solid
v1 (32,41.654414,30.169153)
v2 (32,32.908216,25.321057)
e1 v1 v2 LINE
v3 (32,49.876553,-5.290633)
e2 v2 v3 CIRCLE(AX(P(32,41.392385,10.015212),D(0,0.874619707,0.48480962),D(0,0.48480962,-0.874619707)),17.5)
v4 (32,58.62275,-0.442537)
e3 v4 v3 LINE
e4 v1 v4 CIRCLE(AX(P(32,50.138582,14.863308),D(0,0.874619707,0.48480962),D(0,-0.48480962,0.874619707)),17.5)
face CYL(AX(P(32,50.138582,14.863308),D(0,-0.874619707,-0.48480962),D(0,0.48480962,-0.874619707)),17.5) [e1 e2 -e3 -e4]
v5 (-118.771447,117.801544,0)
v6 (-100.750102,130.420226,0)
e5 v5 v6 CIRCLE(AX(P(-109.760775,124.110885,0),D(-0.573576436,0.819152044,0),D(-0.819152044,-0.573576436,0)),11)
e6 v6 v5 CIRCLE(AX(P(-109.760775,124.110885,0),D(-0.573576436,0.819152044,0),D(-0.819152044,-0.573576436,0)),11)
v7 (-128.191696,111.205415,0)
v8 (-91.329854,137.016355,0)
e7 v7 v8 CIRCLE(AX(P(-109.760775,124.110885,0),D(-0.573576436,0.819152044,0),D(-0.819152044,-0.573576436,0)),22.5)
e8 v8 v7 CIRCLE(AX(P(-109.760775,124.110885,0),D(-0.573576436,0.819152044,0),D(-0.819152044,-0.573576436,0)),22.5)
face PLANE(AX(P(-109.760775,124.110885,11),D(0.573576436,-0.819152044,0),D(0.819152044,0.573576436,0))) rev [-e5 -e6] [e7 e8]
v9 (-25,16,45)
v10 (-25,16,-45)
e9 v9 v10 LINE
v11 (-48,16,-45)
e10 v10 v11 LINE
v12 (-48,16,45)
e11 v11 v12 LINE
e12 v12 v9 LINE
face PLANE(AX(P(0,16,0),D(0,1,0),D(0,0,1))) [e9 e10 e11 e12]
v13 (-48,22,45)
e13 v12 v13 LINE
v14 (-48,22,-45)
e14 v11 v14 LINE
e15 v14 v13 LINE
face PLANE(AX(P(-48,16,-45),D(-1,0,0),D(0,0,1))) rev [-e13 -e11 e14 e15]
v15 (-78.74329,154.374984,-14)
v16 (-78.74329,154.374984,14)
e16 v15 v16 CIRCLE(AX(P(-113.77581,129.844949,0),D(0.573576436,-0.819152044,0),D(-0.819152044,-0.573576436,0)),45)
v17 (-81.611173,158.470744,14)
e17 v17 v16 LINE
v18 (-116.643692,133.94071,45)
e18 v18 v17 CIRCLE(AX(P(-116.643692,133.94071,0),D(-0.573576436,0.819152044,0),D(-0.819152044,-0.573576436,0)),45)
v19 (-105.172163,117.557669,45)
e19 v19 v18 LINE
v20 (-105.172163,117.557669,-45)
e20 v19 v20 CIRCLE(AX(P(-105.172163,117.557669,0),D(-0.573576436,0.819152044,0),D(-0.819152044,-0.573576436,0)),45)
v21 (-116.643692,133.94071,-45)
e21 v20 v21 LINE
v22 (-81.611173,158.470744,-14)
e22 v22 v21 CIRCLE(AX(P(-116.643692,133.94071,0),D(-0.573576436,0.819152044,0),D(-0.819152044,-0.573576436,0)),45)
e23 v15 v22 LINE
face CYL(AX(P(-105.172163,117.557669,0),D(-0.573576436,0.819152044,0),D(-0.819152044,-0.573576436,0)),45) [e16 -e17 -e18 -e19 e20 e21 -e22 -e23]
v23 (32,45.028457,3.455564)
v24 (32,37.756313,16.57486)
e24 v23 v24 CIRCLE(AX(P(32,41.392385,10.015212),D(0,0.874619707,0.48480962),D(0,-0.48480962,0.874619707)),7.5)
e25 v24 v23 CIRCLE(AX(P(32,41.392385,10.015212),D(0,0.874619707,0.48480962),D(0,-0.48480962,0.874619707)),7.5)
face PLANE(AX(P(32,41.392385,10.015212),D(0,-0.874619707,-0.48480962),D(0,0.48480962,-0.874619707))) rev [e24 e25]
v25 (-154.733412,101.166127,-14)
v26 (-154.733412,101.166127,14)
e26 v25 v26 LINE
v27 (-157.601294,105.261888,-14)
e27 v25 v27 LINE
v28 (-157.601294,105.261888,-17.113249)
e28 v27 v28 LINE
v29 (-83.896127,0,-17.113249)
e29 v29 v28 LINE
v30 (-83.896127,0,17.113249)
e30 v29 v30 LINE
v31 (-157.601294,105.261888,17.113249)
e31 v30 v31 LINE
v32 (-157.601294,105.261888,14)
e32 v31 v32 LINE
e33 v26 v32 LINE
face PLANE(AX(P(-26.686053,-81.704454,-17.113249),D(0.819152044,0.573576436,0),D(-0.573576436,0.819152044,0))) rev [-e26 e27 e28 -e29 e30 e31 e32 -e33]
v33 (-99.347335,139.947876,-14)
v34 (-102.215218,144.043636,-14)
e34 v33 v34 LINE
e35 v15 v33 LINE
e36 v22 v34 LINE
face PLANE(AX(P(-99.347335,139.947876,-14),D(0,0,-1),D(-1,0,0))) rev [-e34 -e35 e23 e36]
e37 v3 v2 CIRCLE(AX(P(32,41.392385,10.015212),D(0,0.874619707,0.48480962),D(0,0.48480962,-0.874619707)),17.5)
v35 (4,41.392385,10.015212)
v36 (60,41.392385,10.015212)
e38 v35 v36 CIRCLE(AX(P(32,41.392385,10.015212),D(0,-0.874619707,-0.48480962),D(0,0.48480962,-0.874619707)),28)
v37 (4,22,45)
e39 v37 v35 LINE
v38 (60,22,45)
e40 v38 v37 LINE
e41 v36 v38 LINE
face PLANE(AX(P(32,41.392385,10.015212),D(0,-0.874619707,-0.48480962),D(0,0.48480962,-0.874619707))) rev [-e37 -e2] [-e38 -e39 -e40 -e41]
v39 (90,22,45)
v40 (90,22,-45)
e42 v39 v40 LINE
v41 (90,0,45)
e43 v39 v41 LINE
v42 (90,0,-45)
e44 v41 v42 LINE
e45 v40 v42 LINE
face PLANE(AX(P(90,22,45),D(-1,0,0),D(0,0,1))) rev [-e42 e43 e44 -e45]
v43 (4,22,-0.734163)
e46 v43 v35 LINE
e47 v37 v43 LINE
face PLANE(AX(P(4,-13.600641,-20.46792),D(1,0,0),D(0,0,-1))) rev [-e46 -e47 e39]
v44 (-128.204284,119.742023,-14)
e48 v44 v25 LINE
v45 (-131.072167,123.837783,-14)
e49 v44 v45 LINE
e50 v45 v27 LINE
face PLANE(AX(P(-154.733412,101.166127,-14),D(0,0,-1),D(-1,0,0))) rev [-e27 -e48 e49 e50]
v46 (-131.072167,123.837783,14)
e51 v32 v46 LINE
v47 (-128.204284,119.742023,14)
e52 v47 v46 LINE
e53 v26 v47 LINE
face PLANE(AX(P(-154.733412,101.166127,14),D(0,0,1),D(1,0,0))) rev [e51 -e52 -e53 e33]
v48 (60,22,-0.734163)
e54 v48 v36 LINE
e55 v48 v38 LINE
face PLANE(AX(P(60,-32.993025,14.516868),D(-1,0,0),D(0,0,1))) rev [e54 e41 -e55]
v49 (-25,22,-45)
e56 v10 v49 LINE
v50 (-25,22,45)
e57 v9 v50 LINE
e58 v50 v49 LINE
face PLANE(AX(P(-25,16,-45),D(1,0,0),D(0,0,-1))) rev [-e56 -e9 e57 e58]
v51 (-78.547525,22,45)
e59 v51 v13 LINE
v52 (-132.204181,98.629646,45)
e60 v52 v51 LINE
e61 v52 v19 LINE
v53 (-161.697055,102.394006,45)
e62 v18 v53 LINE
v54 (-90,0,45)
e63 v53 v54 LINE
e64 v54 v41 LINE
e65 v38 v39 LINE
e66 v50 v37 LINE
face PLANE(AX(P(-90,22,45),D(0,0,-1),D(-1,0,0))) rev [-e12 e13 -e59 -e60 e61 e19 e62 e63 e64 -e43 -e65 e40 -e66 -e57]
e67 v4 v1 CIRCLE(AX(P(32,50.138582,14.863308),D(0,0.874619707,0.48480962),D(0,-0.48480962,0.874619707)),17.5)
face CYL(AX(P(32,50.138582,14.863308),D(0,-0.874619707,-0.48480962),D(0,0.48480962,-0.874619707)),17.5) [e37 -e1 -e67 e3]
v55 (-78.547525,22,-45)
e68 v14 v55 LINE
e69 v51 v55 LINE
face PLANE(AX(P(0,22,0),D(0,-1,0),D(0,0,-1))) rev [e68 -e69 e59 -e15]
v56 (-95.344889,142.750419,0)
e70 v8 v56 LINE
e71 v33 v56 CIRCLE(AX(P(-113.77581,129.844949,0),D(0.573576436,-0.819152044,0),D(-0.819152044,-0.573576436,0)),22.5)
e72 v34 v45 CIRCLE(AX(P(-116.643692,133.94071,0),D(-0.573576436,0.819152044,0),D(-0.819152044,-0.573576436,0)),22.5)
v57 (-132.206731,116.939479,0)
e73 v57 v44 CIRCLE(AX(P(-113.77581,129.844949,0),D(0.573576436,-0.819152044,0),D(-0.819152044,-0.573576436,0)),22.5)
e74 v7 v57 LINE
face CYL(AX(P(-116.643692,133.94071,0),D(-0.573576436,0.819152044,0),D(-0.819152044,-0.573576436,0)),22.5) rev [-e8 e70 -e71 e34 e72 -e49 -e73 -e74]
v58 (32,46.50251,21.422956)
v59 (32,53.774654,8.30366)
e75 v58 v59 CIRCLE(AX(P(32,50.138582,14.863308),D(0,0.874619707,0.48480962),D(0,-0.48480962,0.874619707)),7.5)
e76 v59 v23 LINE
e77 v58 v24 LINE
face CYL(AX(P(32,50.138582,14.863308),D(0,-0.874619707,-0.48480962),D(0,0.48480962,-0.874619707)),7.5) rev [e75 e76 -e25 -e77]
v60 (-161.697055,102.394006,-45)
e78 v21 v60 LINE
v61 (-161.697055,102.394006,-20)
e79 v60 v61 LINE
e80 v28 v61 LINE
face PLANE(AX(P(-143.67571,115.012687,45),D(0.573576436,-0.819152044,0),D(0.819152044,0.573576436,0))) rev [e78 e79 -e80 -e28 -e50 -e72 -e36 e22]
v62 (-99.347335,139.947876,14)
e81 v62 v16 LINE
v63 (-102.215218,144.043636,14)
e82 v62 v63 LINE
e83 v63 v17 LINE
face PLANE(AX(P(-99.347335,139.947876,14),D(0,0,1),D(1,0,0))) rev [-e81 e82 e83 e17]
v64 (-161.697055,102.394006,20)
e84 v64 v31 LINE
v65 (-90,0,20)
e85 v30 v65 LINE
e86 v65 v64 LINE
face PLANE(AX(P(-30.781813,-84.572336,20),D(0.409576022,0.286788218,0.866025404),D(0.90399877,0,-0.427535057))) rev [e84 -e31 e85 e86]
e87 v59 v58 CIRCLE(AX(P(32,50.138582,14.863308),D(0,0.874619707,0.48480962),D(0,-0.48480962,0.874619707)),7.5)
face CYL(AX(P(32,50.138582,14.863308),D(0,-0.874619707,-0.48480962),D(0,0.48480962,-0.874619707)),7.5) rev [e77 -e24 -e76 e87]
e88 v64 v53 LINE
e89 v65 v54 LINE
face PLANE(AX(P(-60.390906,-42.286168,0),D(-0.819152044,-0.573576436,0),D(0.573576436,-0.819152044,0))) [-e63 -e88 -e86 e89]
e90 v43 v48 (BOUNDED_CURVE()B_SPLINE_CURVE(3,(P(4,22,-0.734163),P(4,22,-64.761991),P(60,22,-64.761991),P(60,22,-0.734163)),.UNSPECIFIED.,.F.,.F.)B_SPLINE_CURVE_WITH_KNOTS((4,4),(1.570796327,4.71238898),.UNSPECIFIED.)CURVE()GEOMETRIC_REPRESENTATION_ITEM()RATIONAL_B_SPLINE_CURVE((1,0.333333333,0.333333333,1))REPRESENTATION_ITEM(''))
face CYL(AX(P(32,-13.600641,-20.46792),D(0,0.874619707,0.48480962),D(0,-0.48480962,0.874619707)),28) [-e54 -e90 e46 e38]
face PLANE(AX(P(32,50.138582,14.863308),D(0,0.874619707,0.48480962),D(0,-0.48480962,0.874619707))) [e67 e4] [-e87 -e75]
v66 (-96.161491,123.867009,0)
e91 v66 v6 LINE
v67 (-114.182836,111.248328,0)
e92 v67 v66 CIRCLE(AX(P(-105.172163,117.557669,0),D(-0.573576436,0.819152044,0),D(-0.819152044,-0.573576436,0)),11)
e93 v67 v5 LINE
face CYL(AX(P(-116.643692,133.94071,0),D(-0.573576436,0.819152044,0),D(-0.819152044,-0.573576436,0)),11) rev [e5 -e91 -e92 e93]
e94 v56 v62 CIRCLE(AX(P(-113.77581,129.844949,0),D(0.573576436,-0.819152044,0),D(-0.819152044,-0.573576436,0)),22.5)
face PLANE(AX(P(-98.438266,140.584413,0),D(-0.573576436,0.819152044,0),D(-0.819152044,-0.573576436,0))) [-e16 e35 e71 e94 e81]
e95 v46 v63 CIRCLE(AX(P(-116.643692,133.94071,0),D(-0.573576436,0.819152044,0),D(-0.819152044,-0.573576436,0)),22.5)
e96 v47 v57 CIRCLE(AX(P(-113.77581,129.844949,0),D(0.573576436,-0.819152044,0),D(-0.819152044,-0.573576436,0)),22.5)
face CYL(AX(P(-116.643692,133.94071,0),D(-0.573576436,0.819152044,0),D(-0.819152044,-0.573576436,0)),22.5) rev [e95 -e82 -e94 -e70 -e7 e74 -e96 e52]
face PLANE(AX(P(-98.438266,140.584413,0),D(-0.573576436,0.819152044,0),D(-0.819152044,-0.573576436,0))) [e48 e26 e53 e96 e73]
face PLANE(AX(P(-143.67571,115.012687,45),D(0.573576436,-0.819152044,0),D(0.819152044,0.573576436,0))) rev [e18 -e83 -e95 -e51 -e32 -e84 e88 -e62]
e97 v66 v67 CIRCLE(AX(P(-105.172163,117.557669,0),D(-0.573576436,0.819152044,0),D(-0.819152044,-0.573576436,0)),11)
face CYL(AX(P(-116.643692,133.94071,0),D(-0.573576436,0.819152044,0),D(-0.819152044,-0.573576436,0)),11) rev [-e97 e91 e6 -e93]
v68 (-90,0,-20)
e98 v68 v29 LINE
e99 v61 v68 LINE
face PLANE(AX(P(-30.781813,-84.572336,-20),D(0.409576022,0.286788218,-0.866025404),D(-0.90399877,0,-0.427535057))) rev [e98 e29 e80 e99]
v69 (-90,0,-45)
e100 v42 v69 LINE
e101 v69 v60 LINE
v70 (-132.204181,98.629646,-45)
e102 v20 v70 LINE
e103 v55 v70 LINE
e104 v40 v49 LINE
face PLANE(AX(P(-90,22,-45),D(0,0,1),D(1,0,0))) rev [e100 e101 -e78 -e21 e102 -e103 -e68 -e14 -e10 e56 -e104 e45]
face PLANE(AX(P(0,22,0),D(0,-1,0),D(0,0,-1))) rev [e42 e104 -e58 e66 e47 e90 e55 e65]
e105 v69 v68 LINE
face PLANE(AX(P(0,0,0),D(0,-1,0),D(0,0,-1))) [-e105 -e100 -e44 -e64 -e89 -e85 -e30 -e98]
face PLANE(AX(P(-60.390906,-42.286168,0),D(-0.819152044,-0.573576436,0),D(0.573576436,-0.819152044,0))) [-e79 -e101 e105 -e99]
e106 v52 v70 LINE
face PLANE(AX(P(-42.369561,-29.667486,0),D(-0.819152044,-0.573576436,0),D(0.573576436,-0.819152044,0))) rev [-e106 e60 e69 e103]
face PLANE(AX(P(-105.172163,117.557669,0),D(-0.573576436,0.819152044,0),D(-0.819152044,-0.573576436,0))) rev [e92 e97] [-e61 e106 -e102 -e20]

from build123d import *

# Parameters (mm, degrees)
BASE_PLATE_SKETCH_W        = 180
BASE_PLATE_SKETCH_H        = 90
BASE_PLATE_180X90X22_DEPTH = 22
INCLINED_BOSS_BLOCK_REACH  = 118.629
PIVOT_BOSS_SKETCH_R        = 17.5
PIVOT_BOSS_SKETCH_R_2      = 7.5
PIVOT_BOSS_DEPTH           = 10
CROSS_SLOT_SKETCH_W        = 23
CROSS_SLOT_SKETCH_H        = 90
CROSS_SLOT_23X6_DEPTH      = 6
UPRIGHT_ARM_SKETCH_W       = 90
UPRIGHT_ARM_SKETCH_H       = 125
INCLINED_UPRIGHT_ARM_DEPTH = 22
TOP_PAD_DEPTH              = 20
C_BORE_HOLE_22_D           = 22
C_BORE_HOLE_22_DEPTH       = 22.19797288
C_BORE_HOLE_22_CBORE_D     = 45
C_BORE_HOLE_22_CBORE_DEPTH = 12
TOP_PAD_NOTCHES_DEPTH      = 245.0397404
CROSS_RECESS_SKETCH_W      = 32.386085046
CROSS_RECESS_SKETCH_H      = 28
CROSS_RECESS_SKETCH_W_2    = 30
CROSS_RECESS_5_DEEP_DEPTH  = 5


with BuildPart() as part:
    # Base Plate Sketch → Base Plate 180x90x22 (new body)
    with BuildSketch(Plane(origin=(0, 0, 0), x_dir=(1, 0, 0), z_dir=(0, 1, 0))):
        Rectangle(BASE_PLATE_SKETCH_W, BASE_PLATE_SKETCH_H)
    extrude(amount=BASE_PLATE_180X90X22_DEPTH)

    # Inclined Boss Block Sketch → Inclined Boss Block (add, up to next)
    with BuildSketch(Plane(origin=(0, 35.91019407, 19.905345612), x_dir=(-1, 0, 0), z_dir=(0, -0.874619707139395, -0.48480962024633867)), mode=Mode.PRIVATE) as inclined_boss_block_sk1:
        with BuildLine():
            Line((-4, 11.307924824), (-4, -28.692075176))
            Line((-4, -28.692075176), (-60, -28.692075176))
            Line((-60, -28.692075176), (-60, 11.307924824))
            ThreePointArc((-60, 11.307924824), (-32, 39.307924824), (-4, 11.307924824))
        make_face()
    inclined_boss_block_tool1 = extrude(inclined_boss_block_sk1.sketch, amount=INCLINED_BOSS_BLOCK_REACH, mode=Mode.PRIVATE) - part.part
    add(inclined_boss_block_tool1.solids().sort_by_distance((32, 37.179674, 17.615143))[0])

    # Pivot Boss Sketch → Pivot Boss (add)
    with BuildSketch(Plane(origin=(0, 35.91019407, 19.905345612), x_dir=(1, 0, 0), z_dir=(0, 0.8746197071393949, 0.4848096202463387))):
        with Locations(Location((32, 11.307924824, 0), (0, 0, 90))):
            Circle(PIVOT_BOSS_SKETCH_R)
        with Locations(Location((32, 11.307924824, 0), (0, 0, 270))):
            Circle(PIVOT_BOSS_SKETCH_R_2, mode=Mode.SUBTRACT)
    extrude(amount=PIVOT_BOSS_DEPTH)

    # Cross Slot Sketch → Cross Slot 23x6 (cut)
    with BuildSketch(Plane(origin=(0, 22, 0), x_dir=(1, 0, 0), z_dir=(0, 1, 0))):
        with Locations((-36.5, 0)):
            Rectangle(CROSS_SLOT_SKETCH_W, CROSS_SLOT_SKETCH_H)
    extrude(amount=-CROSS_SLOT_23X6_DEPTH, mode=Mode.SUBTRACT)

    # Upright Arm Sketch → Inclined Upright Arm (add)
    with BuildSketch(Plane(origin=(-60.39090645, -42.286167935, 0), x_dir=(0, 0, -1), z_dir=(0.8191520442889931, 0.5735764363510442, 0))):
        with Locations((0, 114.121879272)):
            Rectangle(UPRIGHT_ARM_SKETCH_W, UPRIGHT_ARM_SKETCH_H)
    extrude(amount=INCLINED_UPRIGHT_ARM_DEPTH)

    # Top Pad Sketch → Top Pad (add)
    with BuildSketch(Plane(origin=(-101.306148094, 144.680173471, 0), x_dir=(0.8191520442889931, 0.5735764363510442, 0), z_dir=(-0.5735764363510442, 0.8191520442889931, 0))):
        with BuildLine():
            Line((-18.723683986, 45), (-73.723683986, 45))
            Line((-73.723683986, 45), (-73.723683986, -45))
            Line((-73.723683986, -45), (-18.723683986, -45))
            ThreePointArc((-18.723683986, -45), (26.276316014, 0), (-18.723683986, 45))
        make_face()
    extrude(amount=-TOP_PAD_DEPTH)

    # C-Bore Hole Ø22
    with Locations(Plane(origin=(-101.306148094, 144.680173471, 0), x_dir=(0.8191520442889931, 0.5735764363510442, 0), z_dir=(-0.5735764363510442, 0.8191520442889931, 0))):
        with Locations((-18.723683986, 0)):
            CounterBoreHole(C_BORE_HOLE_22_D / 2, C_BORE_HOLE_22_CBORE_D / 2, C_BORE_HOLE_22_CBORE_DEPTH, depth=C_BORE_HOLE_22_DEPTH)

    # Top Pad Notch Sketch → Top Pad Notches (cut, through all)
    with BuildSketch(Plane(origin=(-101.306148094, 144.680173471, 0), x_dir=(0.8191520442889931, 0.5735764363510442, 0), z_dir=(-0.5735764363510442, 0.8191520442889931, 0))):
        Polygon((-73.723683986, 20), (-68.723683986, 17.113248654), (-68.723683986, -17.113248654), (-73.723683986, -20), align=None)
    extrude(amount=-TOP_PAD_NOTCHES_DEPTH, mode=Mode.SUBTRACT)

    # Cross Recess Sketch → Cross Recess 5 Deep (cut)
    with BuildSketch(Plane(origin=(-101.306148094, 144.680173471, 0), x_dir=(0.8191520442889931, 0.5735764363510442, 0), z_dir=(-0.5735764363510442, 0.8191520442889931, 0))):
        with Locations((-52.530641463, 0)):
            Rectangle(CROSS_RECESS_SKETCH_W, CROSS_RECESS_SKETCH_H)
        with Locations((13.890230968, 0)):
            Rectangle(CROSS_RECESS_SKETCH_W_2, CROSS_RECESS_SKETCH_H)
    extrude(amount=-CROSS_RECESS_5_DEEP_DEPTH, mode=Mode.SUBTRACT)


solid = part.part
